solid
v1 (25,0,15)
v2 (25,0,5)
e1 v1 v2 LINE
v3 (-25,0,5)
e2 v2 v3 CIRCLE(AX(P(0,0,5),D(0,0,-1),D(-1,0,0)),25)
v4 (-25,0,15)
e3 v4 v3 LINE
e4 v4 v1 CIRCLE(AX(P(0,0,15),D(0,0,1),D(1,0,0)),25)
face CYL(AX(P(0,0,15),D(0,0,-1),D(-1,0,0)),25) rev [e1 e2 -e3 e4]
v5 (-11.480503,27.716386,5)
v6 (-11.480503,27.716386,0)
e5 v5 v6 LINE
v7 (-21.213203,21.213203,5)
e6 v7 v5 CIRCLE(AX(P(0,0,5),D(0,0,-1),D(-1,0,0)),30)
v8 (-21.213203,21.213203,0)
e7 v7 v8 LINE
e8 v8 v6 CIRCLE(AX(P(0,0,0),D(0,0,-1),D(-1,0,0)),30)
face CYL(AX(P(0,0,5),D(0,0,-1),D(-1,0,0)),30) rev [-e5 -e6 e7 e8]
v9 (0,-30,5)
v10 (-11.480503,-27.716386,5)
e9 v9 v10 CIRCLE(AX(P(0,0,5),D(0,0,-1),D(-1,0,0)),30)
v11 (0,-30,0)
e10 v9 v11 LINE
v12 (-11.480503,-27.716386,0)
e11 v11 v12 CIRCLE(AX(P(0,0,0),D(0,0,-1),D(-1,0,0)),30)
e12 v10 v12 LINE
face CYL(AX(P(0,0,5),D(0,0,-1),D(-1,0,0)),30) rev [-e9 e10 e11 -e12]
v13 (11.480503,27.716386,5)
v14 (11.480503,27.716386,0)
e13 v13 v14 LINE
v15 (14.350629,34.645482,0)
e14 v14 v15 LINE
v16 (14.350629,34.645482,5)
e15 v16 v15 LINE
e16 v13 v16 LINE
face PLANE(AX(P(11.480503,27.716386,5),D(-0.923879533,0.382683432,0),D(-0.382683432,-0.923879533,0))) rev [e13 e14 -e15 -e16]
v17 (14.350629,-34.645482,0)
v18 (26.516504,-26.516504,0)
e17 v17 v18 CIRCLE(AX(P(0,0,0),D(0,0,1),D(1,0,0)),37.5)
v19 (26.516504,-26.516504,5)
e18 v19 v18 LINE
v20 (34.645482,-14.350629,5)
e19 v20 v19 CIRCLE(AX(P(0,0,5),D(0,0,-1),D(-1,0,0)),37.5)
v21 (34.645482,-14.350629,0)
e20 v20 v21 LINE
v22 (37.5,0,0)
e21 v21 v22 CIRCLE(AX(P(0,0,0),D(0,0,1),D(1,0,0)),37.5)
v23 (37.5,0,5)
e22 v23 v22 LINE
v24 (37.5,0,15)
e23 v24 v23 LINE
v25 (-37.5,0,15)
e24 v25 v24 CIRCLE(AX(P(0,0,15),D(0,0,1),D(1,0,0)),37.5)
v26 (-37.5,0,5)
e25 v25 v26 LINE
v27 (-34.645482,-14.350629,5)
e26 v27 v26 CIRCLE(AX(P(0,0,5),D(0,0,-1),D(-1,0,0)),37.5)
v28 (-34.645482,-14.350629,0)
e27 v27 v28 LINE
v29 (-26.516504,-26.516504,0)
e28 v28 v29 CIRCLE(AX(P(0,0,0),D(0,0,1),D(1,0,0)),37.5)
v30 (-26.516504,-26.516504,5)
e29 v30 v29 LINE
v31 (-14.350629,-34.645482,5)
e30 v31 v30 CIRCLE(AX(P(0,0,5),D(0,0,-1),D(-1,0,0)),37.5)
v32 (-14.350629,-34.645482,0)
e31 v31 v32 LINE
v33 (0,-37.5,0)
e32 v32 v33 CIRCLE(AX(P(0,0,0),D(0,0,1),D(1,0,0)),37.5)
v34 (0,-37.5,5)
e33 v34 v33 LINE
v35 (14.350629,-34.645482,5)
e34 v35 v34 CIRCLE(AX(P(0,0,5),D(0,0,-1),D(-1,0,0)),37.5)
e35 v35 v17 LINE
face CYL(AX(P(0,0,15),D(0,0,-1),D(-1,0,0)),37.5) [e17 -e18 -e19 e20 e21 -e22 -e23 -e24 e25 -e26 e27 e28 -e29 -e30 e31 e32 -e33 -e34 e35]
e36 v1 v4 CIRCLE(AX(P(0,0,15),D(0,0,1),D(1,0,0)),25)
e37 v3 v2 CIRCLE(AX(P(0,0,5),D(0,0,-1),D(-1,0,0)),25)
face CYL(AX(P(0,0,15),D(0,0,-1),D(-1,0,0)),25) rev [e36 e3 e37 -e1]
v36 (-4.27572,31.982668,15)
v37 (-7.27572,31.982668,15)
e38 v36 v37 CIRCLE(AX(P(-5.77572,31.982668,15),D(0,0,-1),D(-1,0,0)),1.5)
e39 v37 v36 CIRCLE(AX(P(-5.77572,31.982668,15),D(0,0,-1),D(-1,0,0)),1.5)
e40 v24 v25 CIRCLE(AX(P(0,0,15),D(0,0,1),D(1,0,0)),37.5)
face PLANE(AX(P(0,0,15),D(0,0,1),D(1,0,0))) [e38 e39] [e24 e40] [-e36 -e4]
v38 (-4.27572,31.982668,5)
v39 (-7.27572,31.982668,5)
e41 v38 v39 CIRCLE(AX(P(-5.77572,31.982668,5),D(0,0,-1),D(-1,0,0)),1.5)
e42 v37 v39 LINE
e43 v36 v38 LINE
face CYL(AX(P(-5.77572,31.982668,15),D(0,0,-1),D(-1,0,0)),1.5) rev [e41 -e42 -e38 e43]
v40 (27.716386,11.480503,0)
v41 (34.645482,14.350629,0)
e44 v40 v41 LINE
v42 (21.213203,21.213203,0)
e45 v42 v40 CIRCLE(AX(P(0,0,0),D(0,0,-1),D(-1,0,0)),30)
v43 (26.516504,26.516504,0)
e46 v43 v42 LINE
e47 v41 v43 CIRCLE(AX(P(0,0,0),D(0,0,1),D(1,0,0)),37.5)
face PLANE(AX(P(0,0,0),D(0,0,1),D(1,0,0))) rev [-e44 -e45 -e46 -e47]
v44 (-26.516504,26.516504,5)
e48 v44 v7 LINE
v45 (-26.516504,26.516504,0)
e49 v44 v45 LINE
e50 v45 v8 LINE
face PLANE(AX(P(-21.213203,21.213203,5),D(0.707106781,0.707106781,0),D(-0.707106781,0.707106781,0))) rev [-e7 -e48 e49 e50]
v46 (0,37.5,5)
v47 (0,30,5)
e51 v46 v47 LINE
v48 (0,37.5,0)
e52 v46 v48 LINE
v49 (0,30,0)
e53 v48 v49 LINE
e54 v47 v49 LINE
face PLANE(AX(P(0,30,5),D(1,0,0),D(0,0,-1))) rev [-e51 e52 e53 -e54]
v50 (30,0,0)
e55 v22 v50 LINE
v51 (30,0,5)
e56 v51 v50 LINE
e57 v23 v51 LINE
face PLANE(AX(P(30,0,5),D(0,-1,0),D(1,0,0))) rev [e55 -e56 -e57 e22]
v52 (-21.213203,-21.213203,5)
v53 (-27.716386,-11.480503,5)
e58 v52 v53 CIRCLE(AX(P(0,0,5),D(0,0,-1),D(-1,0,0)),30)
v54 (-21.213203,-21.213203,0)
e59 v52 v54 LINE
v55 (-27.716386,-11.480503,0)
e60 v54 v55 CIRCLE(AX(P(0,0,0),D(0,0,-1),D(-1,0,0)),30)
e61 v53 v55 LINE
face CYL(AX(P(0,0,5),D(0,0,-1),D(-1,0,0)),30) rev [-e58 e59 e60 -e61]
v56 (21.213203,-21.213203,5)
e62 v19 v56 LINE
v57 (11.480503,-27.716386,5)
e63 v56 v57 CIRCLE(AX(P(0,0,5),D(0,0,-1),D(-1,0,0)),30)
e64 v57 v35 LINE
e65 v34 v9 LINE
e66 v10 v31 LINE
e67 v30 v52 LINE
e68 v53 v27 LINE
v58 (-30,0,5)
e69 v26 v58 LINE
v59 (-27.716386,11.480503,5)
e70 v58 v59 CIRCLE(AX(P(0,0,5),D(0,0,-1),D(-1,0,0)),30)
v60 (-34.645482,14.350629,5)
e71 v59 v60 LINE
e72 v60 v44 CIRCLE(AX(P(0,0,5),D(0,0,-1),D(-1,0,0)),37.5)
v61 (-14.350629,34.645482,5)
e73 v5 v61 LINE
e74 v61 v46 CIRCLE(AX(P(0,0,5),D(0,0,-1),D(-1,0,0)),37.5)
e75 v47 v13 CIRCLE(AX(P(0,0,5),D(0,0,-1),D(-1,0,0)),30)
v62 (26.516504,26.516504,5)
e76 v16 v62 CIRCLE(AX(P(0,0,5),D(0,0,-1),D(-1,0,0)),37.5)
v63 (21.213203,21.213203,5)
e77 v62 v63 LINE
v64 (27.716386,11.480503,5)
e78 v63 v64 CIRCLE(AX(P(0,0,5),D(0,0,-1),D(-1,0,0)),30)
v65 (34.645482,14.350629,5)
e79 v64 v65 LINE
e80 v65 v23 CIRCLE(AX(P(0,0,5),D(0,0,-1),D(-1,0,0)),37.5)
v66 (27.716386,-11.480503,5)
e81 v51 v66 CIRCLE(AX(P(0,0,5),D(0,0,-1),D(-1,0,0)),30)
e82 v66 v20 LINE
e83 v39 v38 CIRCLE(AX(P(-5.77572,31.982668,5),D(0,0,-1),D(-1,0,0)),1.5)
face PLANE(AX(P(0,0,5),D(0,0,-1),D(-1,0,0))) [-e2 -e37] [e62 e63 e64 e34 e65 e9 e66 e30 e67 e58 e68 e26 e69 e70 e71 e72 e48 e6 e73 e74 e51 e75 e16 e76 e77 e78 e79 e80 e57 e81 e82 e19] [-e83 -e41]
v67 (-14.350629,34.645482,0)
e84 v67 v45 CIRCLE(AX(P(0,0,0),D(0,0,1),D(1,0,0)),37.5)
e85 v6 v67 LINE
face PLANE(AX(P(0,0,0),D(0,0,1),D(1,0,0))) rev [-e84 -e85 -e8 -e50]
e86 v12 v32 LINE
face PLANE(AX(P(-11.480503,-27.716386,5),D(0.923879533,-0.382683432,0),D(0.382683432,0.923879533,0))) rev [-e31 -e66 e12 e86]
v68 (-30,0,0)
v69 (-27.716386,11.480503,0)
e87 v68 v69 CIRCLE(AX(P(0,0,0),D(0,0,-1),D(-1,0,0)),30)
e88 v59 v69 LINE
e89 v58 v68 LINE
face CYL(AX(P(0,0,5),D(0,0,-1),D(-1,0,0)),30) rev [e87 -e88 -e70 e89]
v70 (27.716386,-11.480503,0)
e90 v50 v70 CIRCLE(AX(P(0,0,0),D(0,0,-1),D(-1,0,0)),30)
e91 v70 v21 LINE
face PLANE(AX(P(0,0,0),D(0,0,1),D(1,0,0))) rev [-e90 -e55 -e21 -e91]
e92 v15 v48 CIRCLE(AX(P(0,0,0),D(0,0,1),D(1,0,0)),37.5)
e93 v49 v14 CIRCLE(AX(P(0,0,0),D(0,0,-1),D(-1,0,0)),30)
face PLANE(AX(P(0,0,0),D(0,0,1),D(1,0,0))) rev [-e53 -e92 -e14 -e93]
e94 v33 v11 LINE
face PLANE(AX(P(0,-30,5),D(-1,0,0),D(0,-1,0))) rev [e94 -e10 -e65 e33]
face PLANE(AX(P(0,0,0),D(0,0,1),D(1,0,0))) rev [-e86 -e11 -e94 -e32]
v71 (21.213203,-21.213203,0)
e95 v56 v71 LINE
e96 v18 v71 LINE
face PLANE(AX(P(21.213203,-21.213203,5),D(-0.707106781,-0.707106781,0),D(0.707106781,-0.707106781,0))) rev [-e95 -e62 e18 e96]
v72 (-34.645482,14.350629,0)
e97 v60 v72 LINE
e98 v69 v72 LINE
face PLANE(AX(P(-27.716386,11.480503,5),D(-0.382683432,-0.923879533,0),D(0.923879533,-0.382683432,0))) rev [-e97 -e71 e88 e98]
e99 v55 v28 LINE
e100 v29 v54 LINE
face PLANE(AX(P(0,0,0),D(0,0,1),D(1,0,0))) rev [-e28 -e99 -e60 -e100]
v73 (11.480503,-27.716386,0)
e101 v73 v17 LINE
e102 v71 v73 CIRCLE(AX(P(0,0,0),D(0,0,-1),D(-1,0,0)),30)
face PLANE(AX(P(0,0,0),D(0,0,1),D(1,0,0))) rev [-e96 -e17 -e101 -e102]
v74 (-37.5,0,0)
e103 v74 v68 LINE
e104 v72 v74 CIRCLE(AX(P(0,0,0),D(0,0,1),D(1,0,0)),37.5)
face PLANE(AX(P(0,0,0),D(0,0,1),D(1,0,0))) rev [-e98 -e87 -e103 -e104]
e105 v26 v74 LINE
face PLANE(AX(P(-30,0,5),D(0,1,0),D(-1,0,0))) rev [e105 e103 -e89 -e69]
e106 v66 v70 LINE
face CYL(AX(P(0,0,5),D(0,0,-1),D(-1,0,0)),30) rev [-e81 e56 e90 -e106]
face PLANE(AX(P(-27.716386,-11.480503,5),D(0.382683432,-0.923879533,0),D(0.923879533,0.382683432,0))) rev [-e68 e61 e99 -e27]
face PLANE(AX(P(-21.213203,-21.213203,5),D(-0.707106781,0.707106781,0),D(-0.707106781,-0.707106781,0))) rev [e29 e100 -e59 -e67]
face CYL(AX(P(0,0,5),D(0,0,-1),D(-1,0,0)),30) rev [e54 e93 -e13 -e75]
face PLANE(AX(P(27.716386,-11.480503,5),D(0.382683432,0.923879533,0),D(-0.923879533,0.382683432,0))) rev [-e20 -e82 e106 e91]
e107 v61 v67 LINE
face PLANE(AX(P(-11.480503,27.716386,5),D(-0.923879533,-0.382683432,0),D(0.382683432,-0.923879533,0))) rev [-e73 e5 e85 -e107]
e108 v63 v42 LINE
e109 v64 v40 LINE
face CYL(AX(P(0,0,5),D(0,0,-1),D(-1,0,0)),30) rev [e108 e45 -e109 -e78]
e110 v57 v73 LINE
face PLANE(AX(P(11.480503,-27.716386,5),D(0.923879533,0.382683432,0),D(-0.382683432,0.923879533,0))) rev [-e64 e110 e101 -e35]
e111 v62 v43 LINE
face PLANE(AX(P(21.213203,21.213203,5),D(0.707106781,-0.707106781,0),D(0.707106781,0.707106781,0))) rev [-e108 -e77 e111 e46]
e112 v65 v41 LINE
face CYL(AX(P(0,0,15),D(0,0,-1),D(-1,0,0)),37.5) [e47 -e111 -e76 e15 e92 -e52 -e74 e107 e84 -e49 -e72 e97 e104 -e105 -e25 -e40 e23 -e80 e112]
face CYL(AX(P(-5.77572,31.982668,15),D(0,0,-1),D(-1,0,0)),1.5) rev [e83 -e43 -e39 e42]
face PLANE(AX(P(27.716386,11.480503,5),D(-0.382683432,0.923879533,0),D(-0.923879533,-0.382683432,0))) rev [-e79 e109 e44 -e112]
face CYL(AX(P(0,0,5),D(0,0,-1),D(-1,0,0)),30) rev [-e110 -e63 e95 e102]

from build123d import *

# Parameters (mm, degrees)
SKETCH1_R           = 37.5
SKETCH1_R_2         = 25
BOSS_EXTRUDE1_DEPTH = 15
SKETCH2_R           = 30
CUT_EXTRUDE1_DEPTH  = 5
CUT_EXTRUDE2_DEPTH  = 5
SKETCH4_R           = 1.5
CUT_EXTRUDE3_DEPTH  = 10


with BuildPart() as part:
    # Sketch1 → Boss-Extrude1 (new body)
    with BuildSketch(Plane.XY):
        Circle(SKETCH1_R)
        Circle(SKETCH1_R_2, mode=Mode.SUBTRACT)
    extrude(amount=BOSS_EXTRUDE1_DEPTH)

    # Sketch2 → Cut-Extrude1 (cut)
    with BuildSketch(Plane(origin=(0, 0, 0), x_dir=(-1, 0, 0), z_dir=(0, 0, -1))):
        Circle(SKETCH2_R)
    extrude(amount=-CUT_EXTRUDE1_DEPTH, mode=Mode.SUBTRACT)

    # Sketch3 → Cut-Extrude2 (cut)
    with BuildSketch(Plane(origin=(0, 0, 0), x_dir=(-1, 0, 0), z_dir=(0, 0, -1))):
        with BuildLine():
            Line((0, 30), (0, 37.5))
            ThreePointArc((0, 37.5), (7.315887076, 36.779448015), (14.350628714, 34.645482469))
            Line((14.350628714, 34.645482469), (11.480502971, 27.716385975))
            ThreePointArc((11.480502971, 27.716385975), (5.85270966, 29.423558412), (0, 30))
        make_face()
        with BuildLine():
            Line((21.213203436, 21.213203436), (26.516504294, 26.516504294))
            ThreePointArc((26.516504294, 26.516504294), (31.180110461, 20.833883738), (34.645482469, 14.350628714))
            Line((34.645482469, 14.350628714), (27.716385975, 11.480502971))
            ThreePointArc((27.716385975, 11.480502971), (24.944088369, 16.667106991), (21.213203436, 21.213203436))
        make_face()
        with BuildLine():
            Line((30, 0), (37.5, 0))
            ThreePointArc((37.5, 0), (36.779448015, -7.315887076), (34.645482469, -14.350628714))
            Line((34.645482469, -14.350628714), (27.716385975, -11.480502971))
            ThreePointArc((27.716385975, -11.480502971), (29.423558412, -5.85270966), (30, 0))
        make_face()
        with BuildLine():
            Line((21.213203436, -21.213203436), (26.516504294, -26.516504294))
            ThreePointArc((26.516504294, -26.516504294), (20.833883738, -31.180110461), (14.350628714, -34.645482469))
            Line((14.350628714, -34.645482469), (11.480502971, -27.716385975))
            ThreePointArc((11.480502971, -27.716385975), (16.667106991, -24.944088369), (21.213203436, -21.213203436))
        make_face()
        with BuildLine():
            Line((0, -30), (0, -37.5))
            ThreePointArc((0, -37.5), (-7.315887076, -36.779448015), (-14.350628714, -34.645482469))
            Line((-14.350628714, -34.645482469), (-11.480502971, -27.716385975))
            ThreePointArc((-11.480502971, -27.716385975), (-5.85270966, -29.423558412), (0, -30))
        make_face()
        with BuildLine():
            Line((-21.213203436, -21.213203436), (-26.516504294, -26.516504294))
            ThreePointArc((-26.516504294, -26.516504294), (-31.180110461, -20.833883738), (-34.645482469, -14.350628714))
            Line((-34.645482469, -14.350628714), (-27.716385975, -11.480502971))
            ThreePointArc((-27.716385975, -11.480502971), (-24.944088369, -16.667106991), (-21.213203436, -21.213203436))
        make_face()
        with BuildLine():
            Line((-30, 0), (-37.5, 0))
            ThreePointArc((-37.5, 0), (-36.779448015, 7.315887076), (-34.645482469, 14.350628714))
            Line((-34.645482469, 14.350628714), (-27.716385975, 11.480502971))
            ThreePointArc((-27.716385975, 11.480502971), (-29.423558412, 5.85270966), (-30, 0))
        make_face()
        with BuildLine():
            Line((-21.213203436, 21.213203436), (-26.516504294, 26.516504294))
            ThreePointArc((-26.516504294, 26.516504294), (-20.833883738, 31.180110461), (-14.350628714, 34.645482469))
            Line((-14.350628714, 34.645482469), (-11.480502971, 27.716385975))
            ThreePointArc((-11.480502971, 27.716385975), (-16.667106991, 24.944088369), (-21.213203436, 21.213203436))
        make_face()
    extrude(amount=-CUT_EXTRUDE2_DEPTH, mode=Mode.SUBTRACT)

    # Sketch4 → Cut-Extrude3 (cut)
    with BuildSketch(Plane(origin=(0, 0, 5), x_dir=(-1, 0, 0), z_dir=(0, 0, -1))):
        with Locations((5.775719967, 31.982668101)):
            Circle(SKETCH4_R)
    extrude(amount=-CUT_EXTRUDE3_DEPTH, mode=Mode.SUBTRACT)


solid = part.part
